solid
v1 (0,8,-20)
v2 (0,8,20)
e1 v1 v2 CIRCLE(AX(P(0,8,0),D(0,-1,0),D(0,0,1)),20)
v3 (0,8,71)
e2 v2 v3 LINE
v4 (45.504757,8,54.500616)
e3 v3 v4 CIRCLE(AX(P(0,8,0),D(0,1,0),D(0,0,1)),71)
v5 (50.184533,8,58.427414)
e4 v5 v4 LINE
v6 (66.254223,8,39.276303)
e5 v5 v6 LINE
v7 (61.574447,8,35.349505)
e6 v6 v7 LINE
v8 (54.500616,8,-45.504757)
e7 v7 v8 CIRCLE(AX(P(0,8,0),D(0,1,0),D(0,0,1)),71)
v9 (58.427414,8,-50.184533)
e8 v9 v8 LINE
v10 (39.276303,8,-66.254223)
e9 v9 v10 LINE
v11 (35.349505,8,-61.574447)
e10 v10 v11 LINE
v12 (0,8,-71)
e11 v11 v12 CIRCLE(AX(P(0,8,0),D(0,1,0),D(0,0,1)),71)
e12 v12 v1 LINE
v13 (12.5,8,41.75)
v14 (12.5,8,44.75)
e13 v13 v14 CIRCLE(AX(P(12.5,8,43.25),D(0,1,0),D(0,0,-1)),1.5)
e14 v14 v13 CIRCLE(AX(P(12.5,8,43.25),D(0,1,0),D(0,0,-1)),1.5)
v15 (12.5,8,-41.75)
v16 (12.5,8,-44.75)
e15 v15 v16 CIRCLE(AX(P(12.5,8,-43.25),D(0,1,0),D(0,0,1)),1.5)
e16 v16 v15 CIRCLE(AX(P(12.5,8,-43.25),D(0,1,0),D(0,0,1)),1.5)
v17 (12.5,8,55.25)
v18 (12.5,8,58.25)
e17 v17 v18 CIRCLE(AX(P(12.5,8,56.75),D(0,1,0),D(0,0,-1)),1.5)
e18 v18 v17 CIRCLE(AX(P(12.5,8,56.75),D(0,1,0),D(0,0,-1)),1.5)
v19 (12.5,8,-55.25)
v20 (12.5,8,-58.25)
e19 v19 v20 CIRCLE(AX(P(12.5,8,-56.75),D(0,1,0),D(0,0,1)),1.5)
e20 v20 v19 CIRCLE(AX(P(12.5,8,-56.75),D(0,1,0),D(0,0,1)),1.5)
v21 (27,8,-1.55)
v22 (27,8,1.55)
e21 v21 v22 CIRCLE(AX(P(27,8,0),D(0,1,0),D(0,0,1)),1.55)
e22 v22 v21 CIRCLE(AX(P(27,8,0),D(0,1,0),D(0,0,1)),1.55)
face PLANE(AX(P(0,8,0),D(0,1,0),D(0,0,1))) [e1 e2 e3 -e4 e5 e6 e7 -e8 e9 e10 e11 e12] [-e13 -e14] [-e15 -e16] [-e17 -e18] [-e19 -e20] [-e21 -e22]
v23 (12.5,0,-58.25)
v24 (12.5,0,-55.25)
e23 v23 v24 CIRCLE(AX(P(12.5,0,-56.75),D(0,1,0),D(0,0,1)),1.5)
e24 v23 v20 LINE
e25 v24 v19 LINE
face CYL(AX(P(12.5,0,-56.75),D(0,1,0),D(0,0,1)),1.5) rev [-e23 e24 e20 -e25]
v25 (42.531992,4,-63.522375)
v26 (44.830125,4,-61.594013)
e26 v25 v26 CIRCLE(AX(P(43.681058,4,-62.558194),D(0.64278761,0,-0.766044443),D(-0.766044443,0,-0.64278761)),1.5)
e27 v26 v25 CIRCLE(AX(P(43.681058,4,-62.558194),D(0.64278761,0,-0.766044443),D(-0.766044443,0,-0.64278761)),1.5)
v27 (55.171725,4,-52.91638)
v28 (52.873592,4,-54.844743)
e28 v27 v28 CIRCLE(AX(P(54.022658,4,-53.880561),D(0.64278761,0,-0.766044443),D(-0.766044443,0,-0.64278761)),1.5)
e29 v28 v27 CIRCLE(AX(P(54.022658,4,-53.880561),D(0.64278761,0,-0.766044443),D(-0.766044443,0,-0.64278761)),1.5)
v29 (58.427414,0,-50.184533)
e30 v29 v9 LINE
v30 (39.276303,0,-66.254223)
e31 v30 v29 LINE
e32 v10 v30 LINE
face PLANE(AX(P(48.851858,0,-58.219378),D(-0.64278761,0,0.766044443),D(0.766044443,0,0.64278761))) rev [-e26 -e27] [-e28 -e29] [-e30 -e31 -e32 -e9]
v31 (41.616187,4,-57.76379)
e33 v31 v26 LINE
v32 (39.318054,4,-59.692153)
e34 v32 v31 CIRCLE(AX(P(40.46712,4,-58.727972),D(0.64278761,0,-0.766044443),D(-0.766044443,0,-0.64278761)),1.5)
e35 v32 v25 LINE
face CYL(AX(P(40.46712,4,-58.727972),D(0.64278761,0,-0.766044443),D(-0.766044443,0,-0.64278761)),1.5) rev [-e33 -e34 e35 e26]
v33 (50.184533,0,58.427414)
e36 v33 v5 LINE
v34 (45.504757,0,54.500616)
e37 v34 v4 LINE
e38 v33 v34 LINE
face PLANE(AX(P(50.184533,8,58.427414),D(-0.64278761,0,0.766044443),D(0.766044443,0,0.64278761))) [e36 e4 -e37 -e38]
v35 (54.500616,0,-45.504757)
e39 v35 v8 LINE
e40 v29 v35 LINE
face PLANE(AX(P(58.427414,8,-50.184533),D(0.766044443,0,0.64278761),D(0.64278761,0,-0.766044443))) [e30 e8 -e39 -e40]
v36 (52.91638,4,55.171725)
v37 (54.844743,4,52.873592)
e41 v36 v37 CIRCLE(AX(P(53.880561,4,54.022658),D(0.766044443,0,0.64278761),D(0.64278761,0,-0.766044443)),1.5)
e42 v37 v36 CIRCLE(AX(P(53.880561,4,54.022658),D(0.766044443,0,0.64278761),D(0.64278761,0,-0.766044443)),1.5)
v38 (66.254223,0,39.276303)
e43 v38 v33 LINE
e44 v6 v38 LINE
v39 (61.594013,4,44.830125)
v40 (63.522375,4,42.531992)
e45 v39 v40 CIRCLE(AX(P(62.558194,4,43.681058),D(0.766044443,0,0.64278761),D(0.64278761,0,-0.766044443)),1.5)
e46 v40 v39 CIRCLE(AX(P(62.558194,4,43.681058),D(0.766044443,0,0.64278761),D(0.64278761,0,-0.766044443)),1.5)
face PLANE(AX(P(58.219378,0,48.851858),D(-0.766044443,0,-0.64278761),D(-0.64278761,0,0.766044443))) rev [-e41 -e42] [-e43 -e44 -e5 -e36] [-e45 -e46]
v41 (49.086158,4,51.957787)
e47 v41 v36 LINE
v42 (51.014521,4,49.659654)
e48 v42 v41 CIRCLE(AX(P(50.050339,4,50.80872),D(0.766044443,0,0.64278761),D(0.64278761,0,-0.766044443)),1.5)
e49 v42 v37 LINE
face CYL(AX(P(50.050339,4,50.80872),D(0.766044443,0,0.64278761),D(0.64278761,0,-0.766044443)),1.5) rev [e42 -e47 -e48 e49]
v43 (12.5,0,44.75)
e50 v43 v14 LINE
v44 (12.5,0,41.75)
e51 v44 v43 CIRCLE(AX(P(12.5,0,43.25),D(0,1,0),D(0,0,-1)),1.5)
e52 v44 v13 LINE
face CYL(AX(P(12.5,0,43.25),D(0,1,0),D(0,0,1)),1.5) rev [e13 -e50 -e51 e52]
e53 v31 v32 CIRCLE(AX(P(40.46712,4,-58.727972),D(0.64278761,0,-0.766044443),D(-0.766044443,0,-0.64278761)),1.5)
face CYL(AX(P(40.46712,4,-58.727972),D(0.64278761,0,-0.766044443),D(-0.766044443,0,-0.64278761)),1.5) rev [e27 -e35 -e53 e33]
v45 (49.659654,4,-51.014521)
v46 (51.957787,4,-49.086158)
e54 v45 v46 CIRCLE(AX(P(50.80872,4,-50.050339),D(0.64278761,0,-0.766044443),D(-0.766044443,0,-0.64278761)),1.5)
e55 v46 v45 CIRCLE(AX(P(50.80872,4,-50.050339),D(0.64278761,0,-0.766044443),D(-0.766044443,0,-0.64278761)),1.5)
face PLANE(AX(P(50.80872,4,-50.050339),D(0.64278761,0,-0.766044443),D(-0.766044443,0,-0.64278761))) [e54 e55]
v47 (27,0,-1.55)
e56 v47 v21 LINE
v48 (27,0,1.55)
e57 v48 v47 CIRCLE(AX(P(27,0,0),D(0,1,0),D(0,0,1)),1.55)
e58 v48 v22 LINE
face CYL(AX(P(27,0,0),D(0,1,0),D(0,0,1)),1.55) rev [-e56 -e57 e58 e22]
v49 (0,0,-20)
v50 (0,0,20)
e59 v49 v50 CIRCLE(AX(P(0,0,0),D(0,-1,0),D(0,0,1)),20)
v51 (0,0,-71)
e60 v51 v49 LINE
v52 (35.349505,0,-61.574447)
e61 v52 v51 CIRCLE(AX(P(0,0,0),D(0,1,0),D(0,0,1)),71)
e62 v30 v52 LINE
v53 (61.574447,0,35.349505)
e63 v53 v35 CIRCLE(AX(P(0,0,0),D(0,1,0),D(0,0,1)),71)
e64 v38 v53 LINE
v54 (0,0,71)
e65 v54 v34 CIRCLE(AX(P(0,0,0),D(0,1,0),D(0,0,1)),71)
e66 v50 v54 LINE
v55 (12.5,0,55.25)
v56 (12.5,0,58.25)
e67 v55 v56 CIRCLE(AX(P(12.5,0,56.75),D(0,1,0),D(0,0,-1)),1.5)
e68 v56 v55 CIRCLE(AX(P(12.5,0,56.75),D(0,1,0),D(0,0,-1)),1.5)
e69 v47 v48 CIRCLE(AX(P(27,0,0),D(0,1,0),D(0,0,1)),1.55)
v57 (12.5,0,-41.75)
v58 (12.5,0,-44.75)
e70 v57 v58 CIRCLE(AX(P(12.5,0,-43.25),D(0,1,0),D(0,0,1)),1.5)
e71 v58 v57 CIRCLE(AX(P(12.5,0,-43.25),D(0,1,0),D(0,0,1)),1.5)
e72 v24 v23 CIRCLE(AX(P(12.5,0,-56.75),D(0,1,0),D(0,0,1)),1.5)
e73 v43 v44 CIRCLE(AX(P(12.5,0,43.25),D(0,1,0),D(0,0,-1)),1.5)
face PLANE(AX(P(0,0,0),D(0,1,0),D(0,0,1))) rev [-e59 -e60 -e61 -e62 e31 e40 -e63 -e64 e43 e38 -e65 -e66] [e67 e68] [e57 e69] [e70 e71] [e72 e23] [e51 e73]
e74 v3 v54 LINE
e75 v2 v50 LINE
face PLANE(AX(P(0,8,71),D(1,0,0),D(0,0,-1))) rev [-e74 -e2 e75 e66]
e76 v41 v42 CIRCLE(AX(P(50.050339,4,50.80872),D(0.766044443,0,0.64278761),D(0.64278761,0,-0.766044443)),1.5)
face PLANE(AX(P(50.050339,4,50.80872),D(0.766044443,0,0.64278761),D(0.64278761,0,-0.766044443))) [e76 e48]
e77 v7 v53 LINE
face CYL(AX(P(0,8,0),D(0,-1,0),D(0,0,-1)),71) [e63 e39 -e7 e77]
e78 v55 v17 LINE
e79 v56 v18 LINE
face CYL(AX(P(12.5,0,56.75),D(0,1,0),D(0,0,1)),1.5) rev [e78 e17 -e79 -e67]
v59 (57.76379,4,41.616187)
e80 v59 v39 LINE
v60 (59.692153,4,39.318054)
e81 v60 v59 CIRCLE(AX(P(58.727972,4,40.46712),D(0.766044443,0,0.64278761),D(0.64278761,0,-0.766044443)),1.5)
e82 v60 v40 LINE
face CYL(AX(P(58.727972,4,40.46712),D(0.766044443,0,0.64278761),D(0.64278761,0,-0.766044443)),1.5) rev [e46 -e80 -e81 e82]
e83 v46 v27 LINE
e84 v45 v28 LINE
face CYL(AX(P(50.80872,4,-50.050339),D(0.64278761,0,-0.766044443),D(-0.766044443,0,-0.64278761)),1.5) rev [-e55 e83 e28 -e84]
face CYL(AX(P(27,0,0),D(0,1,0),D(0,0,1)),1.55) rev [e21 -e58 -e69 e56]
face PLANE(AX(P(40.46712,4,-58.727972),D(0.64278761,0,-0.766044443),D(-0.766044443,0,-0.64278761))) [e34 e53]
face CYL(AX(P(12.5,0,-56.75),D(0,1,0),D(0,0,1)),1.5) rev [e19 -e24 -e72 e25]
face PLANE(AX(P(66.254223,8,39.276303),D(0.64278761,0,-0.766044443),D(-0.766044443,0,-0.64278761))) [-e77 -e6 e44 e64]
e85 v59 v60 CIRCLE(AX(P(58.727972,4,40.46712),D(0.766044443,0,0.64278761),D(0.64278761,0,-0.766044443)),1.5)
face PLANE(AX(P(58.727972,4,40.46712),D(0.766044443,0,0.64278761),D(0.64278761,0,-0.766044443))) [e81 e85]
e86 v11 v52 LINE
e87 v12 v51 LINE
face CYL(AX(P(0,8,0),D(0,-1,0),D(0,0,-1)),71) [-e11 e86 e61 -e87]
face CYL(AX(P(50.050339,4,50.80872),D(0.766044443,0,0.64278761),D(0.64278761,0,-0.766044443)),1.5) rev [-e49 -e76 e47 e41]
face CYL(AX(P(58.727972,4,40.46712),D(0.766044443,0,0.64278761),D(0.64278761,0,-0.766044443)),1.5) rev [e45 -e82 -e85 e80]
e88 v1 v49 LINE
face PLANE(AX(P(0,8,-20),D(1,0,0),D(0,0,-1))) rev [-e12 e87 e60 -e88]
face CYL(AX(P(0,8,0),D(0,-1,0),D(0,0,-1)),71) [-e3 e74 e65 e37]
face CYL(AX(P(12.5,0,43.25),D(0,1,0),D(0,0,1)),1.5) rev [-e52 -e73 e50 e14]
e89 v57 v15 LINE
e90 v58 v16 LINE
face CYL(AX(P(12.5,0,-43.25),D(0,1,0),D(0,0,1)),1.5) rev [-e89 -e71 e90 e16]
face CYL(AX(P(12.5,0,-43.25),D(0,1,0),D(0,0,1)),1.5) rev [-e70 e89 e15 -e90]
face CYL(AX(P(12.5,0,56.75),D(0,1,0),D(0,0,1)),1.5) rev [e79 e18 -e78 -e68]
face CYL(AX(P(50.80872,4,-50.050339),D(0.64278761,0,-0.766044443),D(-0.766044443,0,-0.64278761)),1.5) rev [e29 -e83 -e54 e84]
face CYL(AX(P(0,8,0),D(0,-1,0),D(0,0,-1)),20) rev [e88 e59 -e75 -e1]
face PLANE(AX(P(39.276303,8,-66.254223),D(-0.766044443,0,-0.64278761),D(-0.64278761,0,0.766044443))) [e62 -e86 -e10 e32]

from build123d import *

# Parameters (mm, degrees)
BOSS_EXTRUDE1_DEPTH = 8
SKETCH2_R           = 1.5
CUT_EXTRUDE1_DEPTH  = 101.727354775
BOSS_EXTRUDE2_START = -71
SKETCH3_W           = 8
SKETCH3_H           = 25
BOSS_EXTRUDE2_DEPTH = 5
SKETCH4_R           = 1.5
CUT_EXTRUDE2_DEPTH  = 5
CIRPATTERN1_COUNT   = 2
CIRPATTERN1_ANGLE   = 90
SKETCH5_R           = 1.55
CUT_EXTRUDE3_DEPTH  = 101.727354775


with BuildPart() as part:
    # Sketch1 → Boss-Extrude1 (new body)
    with BuildSketch(Plane(origin=(0, 0, 0), x_dir=(1, 0, 0), z_dir=(0, 1, 0))):
        with BuildLine():
            Line((0, -71), (0, -20))
            ThreePointArc((0, -20), (20, 0), (0, 20))
            Line((0, 20), (0, 71))
            ThreePointArc((0, 71), (71, 0), (0, -71))
        make_face()
    extrude(amount=BOSS_EXTRUDE1_DEPTH)

    # Sketch2 → Cut-Extrude1 (cut, through all)
    with BuildSketch(Plane(origin=(0, 8, 0), x_dir=(1, 0, 0), z_dir=(0, 1, 0))):
        with Locations(Location((12.5, 43.25, 0), (0, 0, 270))):
            Circle(SKETCH2_R)
        with Locations(Location((12.5, 56.75, 0), (0, 0, 270))):
            Circle(SKETCH2_R)
        with Locations(Location((12.5, -43.25, 0), (0, 0, 90))):
            Circle(SKETCH2_R)
        with Locations(Location((12.5, -56.75, 0), (0, 0, 90))):
            Circle(SKETCH2_R)
    extrude(amount=-CUT_EXTRUDE1_DEPTH, mode=Mode.SUBTRACT)

    # Sketch3 → Boss-Extrude2 (add, symmetric)
    with BuildSketch(Plane(origin=(0, 0, 0), x_dir=(0, -1, 0), z_dir=(-0.6427876096865403, 0, 0.7660444431189772)).offset(BOSS_EXTRUDE2_START)):
        with Locations((-4, 0)):
            Rectangle(SKETCH3_W, SKETCH3_H)
    boss_extrude2 = extrude(amount=BOSS_EXTRUDE2_DEPTH, both=True)

    # Sketch4 → Cut-Extrude2 (cut)
    with BuildSketch(Plane(origin=(48.851858336, 0, -58.219377677), x_dir=(-0.7660444431189772, 0, -0.6427876096865404), z_dir=(0.6427876096865403, 0, -0.7660444431189771))):
        with Locations((-6.75, 4)):
            Circle(SKETCH4_R)
        with Locations((6.75, 4)):
            Circle(SKETCH4_R)
    cut_extrude2 = extrude(amount=-CUT_EXTRUDE2_DEPTH, mode=Mode.SUBTRACT)

    # CirPattern1: Boss-Extrude2, Cut-Extrude2 ×2 about axis
    cirpattern1_axis = Axis((0, 0, 0), (0, -1, 0))
    add([boss_extrude2.rotate(cirpattern1_axis, i * CIRPATTERN1_ANGLE / (CIRPATTERN1_COUNT - 1)) for i in range(1, CIRPATTERN1_COUNT)])
    add([cut_extrude2.rotate(cirpattern1_axis, i * CIRPATTERN1_ANGLE / (CIRPATTERN1_COUNT - 1)) for i in range(1, CIRPATTERN1_COUNT)], mode=Mode.SUBTRACT)

    # Sketch5 → Cut-Extrude3 (cut, through all)
    with BuildSketch(Plane(origin=(0, 8, 0), x_dir=(1, 0, 0), z_dir=(0, 1, 0))):
        with Locations(Location((27, 0, 0), (0, 0, 270))):
            Circle(SKETCH5_R)
    extrude(amount=-CUT_EXTRUDE3_DEPTH, mode=Mode.SUBTRACT)


solid = part.part
